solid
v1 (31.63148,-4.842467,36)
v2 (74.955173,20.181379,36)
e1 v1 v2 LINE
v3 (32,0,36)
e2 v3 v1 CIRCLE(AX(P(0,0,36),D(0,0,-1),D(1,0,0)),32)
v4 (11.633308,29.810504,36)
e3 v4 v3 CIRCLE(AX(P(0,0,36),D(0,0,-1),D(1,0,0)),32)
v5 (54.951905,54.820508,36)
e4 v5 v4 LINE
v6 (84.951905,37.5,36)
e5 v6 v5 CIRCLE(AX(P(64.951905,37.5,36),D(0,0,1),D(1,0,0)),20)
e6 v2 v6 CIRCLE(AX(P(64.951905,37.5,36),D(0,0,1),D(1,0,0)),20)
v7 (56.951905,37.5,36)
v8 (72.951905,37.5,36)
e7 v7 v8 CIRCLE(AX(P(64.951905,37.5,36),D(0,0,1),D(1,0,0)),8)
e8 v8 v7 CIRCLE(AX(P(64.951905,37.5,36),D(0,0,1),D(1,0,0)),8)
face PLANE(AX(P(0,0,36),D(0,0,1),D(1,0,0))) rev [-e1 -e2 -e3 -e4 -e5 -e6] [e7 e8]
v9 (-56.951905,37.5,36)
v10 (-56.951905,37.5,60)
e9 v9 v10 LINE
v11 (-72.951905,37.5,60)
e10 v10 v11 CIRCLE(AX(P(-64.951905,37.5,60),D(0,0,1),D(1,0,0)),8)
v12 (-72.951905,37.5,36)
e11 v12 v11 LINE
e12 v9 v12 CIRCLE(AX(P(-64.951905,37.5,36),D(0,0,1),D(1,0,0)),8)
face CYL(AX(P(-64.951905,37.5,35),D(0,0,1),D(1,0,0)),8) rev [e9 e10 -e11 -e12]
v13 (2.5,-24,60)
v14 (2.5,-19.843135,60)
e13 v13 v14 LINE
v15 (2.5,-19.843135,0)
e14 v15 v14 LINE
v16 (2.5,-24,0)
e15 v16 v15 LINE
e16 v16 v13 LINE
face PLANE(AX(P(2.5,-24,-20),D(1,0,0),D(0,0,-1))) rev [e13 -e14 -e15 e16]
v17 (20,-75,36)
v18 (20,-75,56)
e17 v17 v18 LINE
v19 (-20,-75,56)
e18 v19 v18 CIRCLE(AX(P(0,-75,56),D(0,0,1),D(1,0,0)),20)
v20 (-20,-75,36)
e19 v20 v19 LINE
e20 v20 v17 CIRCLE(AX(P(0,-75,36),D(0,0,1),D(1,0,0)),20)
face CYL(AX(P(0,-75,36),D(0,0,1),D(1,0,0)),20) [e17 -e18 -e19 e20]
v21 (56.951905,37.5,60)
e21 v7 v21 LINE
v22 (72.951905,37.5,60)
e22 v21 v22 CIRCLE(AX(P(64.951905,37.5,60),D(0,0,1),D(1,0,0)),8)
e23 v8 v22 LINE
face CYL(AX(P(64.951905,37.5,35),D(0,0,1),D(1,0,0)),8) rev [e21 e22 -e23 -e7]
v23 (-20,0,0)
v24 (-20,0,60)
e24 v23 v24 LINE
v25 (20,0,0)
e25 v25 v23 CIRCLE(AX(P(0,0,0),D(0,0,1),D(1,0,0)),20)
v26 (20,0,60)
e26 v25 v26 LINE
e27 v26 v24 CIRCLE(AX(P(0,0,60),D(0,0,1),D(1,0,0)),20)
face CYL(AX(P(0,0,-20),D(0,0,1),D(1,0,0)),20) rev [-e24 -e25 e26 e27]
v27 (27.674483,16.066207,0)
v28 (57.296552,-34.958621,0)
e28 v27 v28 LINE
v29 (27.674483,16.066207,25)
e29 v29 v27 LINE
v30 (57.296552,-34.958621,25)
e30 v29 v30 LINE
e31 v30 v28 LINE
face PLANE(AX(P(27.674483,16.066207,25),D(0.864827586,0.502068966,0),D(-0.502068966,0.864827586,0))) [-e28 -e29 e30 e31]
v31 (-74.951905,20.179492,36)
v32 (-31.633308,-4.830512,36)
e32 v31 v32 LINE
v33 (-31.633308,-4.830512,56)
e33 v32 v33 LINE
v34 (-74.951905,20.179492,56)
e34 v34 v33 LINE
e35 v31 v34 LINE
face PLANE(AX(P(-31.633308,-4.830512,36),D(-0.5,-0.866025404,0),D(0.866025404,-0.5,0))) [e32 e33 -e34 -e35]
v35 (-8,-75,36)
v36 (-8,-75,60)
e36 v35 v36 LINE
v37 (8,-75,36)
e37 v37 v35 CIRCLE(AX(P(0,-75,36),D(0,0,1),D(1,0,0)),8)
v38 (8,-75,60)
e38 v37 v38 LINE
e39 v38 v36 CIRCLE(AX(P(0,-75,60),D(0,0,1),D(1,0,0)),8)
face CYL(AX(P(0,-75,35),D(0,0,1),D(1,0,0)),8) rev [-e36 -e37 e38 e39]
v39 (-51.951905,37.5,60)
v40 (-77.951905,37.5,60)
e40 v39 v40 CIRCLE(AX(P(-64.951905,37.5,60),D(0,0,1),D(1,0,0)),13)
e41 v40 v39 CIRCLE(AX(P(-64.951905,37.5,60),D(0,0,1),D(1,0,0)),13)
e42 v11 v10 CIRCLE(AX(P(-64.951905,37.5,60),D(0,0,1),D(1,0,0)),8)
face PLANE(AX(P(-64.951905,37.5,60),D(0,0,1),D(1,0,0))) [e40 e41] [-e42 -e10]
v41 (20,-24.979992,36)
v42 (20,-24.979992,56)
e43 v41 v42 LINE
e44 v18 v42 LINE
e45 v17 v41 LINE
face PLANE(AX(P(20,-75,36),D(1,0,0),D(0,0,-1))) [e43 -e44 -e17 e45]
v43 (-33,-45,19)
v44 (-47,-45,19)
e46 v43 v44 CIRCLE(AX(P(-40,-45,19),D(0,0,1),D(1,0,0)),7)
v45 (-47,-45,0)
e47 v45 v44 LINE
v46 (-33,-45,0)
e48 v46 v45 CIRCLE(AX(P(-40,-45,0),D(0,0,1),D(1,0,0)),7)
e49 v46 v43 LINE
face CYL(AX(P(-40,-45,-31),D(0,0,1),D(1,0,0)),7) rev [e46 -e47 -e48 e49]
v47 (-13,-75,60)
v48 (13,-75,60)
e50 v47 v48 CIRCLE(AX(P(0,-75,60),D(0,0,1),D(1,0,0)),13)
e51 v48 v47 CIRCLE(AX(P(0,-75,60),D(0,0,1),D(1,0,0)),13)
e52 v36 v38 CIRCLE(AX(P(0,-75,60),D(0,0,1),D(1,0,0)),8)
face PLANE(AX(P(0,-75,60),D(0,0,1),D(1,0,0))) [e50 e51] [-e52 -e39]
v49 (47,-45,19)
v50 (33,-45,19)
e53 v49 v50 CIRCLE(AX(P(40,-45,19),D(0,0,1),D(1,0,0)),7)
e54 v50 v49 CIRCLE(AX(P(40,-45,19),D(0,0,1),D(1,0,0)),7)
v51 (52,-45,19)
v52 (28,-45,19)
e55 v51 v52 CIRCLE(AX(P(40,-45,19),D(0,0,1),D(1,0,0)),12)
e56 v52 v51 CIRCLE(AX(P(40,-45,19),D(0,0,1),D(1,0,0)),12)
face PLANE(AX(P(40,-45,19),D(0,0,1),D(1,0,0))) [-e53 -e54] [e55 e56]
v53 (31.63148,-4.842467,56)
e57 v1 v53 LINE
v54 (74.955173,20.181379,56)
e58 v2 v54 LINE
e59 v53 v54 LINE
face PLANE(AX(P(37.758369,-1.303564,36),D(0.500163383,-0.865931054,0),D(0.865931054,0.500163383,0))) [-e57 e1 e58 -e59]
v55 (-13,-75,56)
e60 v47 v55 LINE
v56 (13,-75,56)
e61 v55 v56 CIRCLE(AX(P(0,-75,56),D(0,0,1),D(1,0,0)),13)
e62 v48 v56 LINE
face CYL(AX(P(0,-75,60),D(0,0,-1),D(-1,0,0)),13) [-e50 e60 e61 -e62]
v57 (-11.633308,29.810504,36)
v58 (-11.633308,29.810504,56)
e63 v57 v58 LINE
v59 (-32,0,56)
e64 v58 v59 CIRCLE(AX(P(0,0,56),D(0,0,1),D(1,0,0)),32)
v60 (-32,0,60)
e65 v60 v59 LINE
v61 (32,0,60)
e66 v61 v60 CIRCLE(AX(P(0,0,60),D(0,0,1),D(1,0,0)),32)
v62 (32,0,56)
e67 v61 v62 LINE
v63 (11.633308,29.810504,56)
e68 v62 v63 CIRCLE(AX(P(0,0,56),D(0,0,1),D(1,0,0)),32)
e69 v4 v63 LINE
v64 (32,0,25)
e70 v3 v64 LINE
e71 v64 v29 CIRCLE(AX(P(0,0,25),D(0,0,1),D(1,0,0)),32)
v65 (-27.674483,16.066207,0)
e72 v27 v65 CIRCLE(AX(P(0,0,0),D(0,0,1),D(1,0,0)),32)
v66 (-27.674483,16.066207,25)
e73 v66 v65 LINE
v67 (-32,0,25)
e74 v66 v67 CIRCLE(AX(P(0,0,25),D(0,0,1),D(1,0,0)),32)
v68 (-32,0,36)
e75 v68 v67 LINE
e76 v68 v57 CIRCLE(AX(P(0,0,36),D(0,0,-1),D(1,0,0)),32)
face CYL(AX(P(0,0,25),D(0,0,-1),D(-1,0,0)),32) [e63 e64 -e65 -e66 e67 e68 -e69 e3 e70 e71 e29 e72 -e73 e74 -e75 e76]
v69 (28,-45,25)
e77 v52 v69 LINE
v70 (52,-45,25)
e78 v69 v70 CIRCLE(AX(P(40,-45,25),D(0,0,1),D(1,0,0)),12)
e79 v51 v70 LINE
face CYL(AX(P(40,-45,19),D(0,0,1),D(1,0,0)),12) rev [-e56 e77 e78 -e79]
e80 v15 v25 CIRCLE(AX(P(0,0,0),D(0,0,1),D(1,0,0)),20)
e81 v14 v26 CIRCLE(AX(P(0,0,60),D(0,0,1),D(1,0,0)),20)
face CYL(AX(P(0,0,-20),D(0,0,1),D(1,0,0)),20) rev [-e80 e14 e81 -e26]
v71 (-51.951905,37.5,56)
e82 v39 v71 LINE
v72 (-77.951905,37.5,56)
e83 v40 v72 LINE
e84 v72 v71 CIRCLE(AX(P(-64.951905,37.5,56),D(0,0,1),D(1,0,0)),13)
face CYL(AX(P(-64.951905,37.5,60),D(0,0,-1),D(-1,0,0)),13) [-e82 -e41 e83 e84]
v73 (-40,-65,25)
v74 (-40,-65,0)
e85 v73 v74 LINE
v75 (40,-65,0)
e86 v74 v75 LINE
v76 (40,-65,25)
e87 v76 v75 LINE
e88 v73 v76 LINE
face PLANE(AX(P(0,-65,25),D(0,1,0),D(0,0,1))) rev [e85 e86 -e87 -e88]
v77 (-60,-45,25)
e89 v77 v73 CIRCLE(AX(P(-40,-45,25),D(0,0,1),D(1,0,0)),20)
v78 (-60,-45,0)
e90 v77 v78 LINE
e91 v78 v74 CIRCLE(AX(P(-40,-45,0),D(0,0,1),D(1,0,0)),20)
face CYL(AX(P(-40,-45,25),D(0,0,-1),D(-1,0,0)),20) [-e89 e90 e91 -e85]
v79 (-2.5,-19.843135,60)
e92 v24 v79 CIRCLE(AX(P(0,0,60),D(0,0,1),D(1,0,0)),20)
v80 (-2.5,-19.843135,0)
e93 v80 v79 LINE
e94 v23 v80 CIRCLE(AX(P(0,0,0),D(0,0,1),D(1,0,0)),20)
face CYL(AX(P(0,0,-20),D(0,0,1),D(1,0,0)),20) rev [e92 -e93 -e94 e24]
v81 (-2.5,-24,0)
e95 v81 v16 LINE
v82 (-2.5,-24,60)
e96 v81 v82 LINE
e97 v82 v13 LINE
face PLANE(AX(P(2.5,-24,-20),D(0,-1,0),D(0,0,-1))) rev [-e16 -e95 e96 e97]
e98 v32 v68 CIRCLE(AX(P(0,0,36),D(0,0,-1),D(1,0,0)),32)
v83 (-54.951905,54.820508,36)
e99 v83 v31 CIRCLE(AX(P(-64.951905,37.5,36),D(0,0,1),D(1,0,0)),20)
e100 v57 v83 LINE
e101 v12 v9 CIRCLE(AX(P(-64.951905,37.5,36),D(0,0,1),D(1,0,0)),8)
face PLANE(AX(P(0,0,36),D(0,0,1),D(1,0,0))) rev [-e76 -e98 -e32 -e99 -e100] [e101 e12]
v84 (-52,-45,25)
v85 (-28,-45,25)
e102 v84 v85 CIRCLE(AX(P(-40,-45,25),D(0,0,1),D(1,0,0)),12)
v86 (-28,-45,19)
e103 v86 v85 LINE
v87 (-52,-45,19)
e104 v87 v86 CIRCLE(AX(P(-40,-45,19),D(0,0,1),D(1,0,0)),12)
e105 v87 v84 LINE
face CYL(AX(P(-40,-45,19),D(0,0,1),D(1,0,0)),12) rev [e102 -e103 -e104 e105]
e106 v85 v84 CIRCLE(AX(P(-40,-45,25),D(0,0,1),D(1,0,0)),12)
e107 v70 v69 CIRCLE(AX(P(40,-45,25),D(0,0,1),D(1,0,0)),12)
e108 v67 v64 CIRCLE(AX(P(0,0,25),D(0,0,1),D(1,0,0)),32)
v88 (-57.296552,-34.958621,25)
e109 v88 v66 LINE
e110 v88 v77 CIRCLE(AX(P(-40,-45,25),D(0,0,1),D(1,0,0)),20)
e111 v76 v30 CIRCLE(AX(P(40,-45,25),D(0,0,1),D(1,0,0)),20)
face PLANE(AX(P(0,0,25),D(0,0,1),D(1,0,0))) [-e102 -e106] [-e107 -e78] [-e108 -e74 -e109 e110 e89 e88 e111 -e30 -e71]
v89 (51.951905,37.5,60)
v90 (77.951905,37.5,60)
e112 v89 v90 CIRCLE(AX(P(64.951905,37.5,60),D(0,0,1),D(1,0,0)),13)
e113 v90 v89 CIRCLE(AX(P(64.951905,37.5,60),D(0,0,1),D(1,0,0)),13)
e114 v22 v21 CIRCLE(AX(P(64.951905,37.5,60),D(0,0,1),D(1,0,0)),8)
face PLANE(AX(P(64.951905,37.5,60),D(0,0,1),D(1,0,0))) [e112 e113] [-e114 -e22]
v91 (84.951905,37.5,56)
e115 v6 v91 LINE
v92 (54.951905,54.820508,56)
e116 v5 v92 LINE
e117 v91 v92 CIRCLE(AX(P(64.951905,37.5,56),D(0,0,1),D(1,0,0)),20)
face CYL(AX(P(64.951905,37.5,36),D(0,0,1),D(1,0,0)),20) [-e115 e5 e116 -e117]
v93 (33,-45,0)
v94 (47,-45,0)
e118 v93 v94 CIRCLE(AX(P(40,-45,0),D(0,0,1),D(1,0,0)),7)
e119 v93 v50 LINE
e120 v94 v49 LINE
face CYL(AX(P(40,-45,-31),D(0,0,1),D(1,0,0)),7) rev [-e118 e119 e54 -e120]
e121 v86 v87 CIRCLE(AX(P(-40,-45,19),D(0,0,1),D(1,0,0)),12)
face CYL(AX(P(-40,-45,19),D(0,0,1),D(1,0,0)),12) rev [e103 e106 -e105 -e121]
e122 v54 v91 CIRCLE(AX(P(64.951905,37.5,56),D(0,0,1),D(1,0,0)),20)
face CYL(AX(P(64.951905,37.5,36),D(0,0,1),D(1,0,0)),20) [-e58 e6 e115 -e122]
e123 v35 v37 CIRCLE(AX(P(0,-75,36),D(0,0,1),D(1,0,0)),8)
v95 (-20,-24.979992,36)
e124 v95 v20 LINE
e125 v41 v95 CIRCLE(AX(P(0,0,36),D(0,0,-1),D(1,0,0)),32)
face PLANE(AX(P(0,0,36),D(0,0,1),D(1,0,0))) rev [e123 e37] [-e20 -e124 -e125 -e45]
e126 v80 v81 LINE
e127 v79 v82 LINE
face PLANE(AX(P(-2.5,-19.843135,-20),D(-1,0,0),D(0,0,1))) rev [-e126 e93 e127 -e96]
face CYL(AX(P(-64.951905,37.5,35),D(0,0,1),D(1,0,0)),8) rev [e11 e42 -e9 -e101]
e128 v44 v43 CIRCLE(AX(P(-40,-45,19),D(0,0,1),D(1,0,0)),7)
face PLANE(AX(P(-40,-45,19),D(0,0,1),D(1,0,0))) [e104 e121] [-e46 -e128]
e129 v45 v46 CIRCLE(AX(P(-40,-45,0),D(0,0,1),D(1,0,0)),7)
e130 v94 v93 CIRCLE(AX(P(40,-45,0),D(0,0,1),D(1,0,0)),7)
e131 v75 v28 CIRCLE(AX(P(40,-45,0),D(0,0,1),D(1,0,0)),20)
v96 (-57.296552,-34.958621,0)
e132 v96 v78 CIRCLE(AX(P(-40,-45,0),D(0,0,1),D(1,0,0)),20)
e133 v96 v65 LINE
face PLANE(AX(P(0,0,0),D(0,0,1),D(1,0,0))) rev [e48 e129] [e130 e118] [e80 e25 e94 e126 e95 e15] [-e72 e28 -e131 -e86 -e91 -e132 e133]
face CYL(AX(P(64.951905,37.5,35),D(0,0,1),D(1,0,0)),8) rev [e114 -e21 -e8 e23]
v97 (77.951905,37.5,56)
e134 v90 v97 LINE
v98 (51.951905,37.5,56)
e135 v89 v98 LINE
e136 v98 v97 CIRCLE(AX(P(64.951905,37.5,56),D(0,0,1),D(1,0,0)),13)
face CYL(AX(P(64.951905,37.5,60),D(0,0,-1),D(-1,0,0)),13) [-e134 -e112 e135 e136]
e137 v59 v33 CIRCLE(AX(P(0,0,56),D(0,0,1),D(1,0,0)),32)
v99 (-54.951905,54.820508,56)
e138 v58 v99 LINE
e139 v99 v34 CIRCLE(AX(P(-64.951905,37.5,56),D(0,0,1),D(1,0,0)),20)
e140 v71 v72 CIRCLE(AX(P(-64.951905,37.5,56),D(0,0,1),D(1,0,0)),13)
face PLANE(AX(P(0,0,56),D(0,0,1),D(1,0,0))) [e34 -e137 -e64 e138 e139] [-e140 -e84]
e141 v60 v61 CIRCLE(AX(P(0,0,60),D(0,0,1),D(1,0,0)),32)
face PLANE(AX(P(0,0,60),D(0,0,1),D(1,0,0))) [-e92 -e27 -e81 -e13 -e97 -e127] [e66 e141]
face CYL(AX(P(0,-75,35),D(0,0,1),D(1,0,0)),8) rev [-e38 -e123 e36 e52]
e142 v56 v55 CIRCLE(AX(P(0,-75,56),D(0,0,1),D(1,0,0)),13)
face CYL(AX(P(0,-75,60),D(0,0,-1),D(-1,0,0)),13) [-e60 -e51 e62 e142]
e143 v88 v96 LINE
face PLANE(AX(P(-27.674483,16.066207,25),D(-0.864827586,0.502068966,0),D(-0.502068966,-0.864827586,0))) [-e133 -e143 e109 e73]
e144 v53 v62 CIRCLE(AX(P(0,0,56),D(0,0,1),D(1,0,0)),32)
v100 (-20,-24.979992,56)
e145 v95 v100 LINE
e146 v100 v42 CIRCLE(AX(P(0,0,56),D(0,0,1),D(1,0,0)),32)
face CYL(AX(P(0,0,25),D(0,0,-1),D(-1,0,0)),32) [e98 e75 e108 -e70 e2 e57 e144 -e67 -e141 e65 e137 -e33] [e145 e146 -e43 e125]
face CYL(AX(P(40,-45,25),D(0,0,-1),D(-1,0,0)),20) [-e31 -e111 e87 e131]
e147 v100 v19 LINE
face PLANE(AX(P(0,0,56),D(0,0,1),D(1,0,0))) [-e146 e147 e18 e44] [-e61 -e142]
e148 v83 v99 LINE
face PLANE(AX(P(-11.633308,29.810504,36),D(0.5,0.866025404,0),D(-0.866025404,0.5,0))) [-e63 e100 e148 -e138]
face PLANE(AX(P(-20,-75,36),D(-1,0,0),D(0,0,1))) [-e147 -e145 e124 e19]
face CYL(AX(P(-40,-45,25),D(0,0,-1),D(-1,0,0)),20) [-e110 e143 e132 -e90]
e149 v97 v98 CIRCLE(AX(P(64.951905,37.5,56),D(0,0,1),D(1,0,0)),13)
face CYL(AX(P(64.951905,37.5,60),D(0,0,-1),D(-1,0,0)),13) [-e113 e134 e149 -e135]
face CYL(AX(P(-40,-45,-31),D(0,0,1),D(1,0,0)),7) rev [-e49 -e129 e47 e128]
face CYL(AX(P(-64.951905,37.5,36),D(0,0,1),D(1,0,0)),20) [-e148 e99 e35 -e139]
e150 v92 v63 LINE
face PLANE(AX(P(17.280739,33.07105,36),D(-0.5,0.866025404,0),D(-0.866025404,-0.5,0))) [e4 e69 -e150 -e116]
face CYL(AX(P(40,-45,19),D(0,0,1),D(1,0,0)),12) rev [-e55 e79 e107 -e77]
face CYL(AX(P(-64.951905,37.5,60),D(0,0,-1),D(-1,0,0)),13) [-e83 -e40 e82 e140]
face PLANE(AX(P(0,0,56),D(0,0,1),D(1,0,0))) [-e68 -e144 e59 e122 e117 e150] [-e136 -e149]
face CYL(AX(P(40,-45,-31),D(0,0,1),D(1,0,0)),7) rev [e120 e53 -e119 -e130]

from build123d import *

# Parameters (mm, degrees)
BASE_BLOCK_DEPTH            = 25
HUB_SKETCH_64_R             = 32
HUB_64_DEPTH                = 31
THREE_START                 = -20
THREE_ARMS_120DEG_DEPTH     = 20
HUB_COLLAR_SKETCH_64_R      = 32
HUB_COLLAR_64X4_DEPTH       = 4
BOLT_BOSSES_SKETCH_3X_13_R  = 13
BOLT_BOSSES_3X_13_DEPTH     = 4
BOLT_HOLES_SKETCH_3X_8_R    = 8
BOLT_HOLES_3X_8_DEPTH       = 25
KEYED_BORE_24_DEPTH         = 80
COUNTERBORE_SKETCH_2X_12_R  = 12
COUNTERBORES_2X_12X6_DEPTH  = 6
THROUGH_HOLES_SKETCH_2X_7_R = 7
THROUGH_HOLES_2X_7_DEPTH    = 50


with BuildPart() as part:
    # Base Block Sketch → Base Block (new body)
    with BuildSketch(Plane.XY):
        with BuildLine():
            Line((-57.296551724, -34.95862069), (-27.674482759, 16.066206897))
            ThreePointArc((-27.674482759, 16.066206897), (0, 32), (27.674482759, 16.066206897))
            Line((27.674482759, 16.066206897), (57.296551724, -34.95862069))
            ThreePointArc((57.296551724, -34.95862069), (57.332449137, -54.979288897), (40, -65))
            Line((40, -65), (-40, -65))
            ThreePointArc((-40, -65), (-57.332449137, -54.979288897), (-57.296551724, -34.95862069))
        make_face()
    extrude(amount=BASE_BLOCK_DEPTH)

    # Hub Sketch _64 → Hub _64 (add)
    with BuildSketch(Plane.XY.offset(25)):
        with Locations(Location((0, 0, 0), (0, 0, 149.863023681))):
            Circle(HUB_SKETCH_64_R)
    extrude(amount=HUB_64_DEPTH)

    # Three Arms Sketch → Three Arms 120deg (add)
    with BuildSketch(Plane.XY.offset(56).offset(THREE_START)):
        with BuildLine():
            Line((-20, -75), (-20, -24.979991994))
            ThreePointArc((-20, -24.979991994), (0, -32), (20, -24.979991994))
            Line((20, -24.979991994), (20, -75))
            ThreePointArc((20, -75), (0, -95), (-20, -75))
        make_face()
        with BuildLine():
            Line((-11.633307653, 29.810504072), (-54.951905284, 54.820508076))
            ThreePointArc((-54.951905284, 54.820508076), (-82.27241336, 47.5), (-74.951905284, 20.179491924))
            Line((-74.951905284, 20.179491924), (-31.633307653, -4.830512079))
            ThreePointArc((-31.633307653, -4.830512079), (-27.712812921, 16), (-11.633307653, 29.810504072))
        make_face()
        with BuildLine():
            Line((17.280738855, 33.071049997), (54.951905284, 54.820508076))
            ThreePointArc((54.951905284, 54.820508076), (82.27146994, 47.501633873), (74.955172941, 20.181378918))
            Line((74.955172941, 20.181378918), (37.758368932, -1.303564067))
            Line((37.758368932, -1.303564067), (31.631479851, -4.842466563))
            ThreePointArc((31.631479851, -4.842466563), (27.715835779, 15.994763115), (11.633307653, 29.810504072))
            Line((11.633307653, 29.810504072), (17.280738855, 33.071049997))
        make_face()
    extrude(amount=THREE_ARMS_120DEG_DEPTH)

    # Hub Collar Sketch _64 → Hub Collar _64x4 (add)
    with BuildSketch(Plane.XY.offset(56)):
        with Locations(Location((0, 0, 0), (0, 0, 149.863023681))):
            Circle(HUB_COLLAR_SKETCH_64_R)
    extrude(amount=HUB_COLLAR_64X4_DEPTH)

    # Bolt Bosses Sketch 3x_13 → Bolt Bosses 3x_13 (add)
    with BuildSketch(Plane.XY.offset(56)):
        with Locations((-64.951905284, 37.5)):
            Circle(BOLT_BOSSES_SKETCH_3X_13_R)
        with Locations((64.951905284, 37.5)):
            Circle(BOLT_BOSSES_SKETCH_3X_13_R)
        with Locations((0, -75)):
            Circle(BOLT_BOSSES_SKETCH_3X_13_R)
    extrude(amount=BOLT_BOSSES_3X_13_DEPTH)

    # Bolt Holes Sketch 3x_8 → Bolt Holes 3x_8 (cut)
    with BuildSketch(Plane.XY.offset(60)):
        with Locations((-64.951905284, 37.5)):
            Circle(BOLT_HOLES_SKETCH_3X_8_R)
        with Locations((64.951905284, 37.5)):
            Circle(BOLT_HOLES_SKETCH_3X_8_R)
        with Locations((0, -75)):
            Circle(BOLT_HOLES_SKETCH_3X_8_R)
    extrude(amount=-BOLT_HOLES_3X_8_DEPTH, mode=Mode.SUBTRACT)

    # Keyed Bore Sketch _24 → Keyed Bore _24 (cut)
    with BuildSketch(Plane.XY.offset(60)):
        with BuildLine():
            Line((2.5, -24), (-2.5, -24))
            Line((-2.5, -24), (-2.5, -19.843134833))
            ThreePointArc((-2.5, -19.843134833), (0, 20), (2.5, -19.843134833))
            Line((2.5, -19.843134833), (2.5, -24))
        make_face()
    extrude(amount=-KEYED_BORE_24_DEPTH, mode=Mode.SUBTRACT)

    # Counterbore Sketch 2x_12 → Counterbores 2x_12x6 (cut)
    with BuildSketch(Plane.XY.offset(25)):
        with Locations((-40, -45)):
            Circle(COUNTERBORE_SKETCH_2X_12_R)
        with Locations((40, -45)):
            Circle(COUNTERBORE_SKETCH_2X_12_R)
    extrude(amount=-COUNTERBORES_2X_12X6_DEPTH, mode=Mode.SUBTRACT)

    # Through Holes Sketch 2x_7 → Through Holes 2x_7 (cut)
    with BuildSketch(Plane.XY.offset(19)):
        with Locations((-40, -45)):
            Circle(THROUGH_HOLES_SKETCH_2X_7_R)
        with Locations((40, -45)):
            Circle(THROUGH_HOLES_SKETCH_2X_7_R)
    extrude(amount=-THROUGH_HOLES_2X_7_DEPTH, mode=Mode.SUBTRACT)


solid = part.part
